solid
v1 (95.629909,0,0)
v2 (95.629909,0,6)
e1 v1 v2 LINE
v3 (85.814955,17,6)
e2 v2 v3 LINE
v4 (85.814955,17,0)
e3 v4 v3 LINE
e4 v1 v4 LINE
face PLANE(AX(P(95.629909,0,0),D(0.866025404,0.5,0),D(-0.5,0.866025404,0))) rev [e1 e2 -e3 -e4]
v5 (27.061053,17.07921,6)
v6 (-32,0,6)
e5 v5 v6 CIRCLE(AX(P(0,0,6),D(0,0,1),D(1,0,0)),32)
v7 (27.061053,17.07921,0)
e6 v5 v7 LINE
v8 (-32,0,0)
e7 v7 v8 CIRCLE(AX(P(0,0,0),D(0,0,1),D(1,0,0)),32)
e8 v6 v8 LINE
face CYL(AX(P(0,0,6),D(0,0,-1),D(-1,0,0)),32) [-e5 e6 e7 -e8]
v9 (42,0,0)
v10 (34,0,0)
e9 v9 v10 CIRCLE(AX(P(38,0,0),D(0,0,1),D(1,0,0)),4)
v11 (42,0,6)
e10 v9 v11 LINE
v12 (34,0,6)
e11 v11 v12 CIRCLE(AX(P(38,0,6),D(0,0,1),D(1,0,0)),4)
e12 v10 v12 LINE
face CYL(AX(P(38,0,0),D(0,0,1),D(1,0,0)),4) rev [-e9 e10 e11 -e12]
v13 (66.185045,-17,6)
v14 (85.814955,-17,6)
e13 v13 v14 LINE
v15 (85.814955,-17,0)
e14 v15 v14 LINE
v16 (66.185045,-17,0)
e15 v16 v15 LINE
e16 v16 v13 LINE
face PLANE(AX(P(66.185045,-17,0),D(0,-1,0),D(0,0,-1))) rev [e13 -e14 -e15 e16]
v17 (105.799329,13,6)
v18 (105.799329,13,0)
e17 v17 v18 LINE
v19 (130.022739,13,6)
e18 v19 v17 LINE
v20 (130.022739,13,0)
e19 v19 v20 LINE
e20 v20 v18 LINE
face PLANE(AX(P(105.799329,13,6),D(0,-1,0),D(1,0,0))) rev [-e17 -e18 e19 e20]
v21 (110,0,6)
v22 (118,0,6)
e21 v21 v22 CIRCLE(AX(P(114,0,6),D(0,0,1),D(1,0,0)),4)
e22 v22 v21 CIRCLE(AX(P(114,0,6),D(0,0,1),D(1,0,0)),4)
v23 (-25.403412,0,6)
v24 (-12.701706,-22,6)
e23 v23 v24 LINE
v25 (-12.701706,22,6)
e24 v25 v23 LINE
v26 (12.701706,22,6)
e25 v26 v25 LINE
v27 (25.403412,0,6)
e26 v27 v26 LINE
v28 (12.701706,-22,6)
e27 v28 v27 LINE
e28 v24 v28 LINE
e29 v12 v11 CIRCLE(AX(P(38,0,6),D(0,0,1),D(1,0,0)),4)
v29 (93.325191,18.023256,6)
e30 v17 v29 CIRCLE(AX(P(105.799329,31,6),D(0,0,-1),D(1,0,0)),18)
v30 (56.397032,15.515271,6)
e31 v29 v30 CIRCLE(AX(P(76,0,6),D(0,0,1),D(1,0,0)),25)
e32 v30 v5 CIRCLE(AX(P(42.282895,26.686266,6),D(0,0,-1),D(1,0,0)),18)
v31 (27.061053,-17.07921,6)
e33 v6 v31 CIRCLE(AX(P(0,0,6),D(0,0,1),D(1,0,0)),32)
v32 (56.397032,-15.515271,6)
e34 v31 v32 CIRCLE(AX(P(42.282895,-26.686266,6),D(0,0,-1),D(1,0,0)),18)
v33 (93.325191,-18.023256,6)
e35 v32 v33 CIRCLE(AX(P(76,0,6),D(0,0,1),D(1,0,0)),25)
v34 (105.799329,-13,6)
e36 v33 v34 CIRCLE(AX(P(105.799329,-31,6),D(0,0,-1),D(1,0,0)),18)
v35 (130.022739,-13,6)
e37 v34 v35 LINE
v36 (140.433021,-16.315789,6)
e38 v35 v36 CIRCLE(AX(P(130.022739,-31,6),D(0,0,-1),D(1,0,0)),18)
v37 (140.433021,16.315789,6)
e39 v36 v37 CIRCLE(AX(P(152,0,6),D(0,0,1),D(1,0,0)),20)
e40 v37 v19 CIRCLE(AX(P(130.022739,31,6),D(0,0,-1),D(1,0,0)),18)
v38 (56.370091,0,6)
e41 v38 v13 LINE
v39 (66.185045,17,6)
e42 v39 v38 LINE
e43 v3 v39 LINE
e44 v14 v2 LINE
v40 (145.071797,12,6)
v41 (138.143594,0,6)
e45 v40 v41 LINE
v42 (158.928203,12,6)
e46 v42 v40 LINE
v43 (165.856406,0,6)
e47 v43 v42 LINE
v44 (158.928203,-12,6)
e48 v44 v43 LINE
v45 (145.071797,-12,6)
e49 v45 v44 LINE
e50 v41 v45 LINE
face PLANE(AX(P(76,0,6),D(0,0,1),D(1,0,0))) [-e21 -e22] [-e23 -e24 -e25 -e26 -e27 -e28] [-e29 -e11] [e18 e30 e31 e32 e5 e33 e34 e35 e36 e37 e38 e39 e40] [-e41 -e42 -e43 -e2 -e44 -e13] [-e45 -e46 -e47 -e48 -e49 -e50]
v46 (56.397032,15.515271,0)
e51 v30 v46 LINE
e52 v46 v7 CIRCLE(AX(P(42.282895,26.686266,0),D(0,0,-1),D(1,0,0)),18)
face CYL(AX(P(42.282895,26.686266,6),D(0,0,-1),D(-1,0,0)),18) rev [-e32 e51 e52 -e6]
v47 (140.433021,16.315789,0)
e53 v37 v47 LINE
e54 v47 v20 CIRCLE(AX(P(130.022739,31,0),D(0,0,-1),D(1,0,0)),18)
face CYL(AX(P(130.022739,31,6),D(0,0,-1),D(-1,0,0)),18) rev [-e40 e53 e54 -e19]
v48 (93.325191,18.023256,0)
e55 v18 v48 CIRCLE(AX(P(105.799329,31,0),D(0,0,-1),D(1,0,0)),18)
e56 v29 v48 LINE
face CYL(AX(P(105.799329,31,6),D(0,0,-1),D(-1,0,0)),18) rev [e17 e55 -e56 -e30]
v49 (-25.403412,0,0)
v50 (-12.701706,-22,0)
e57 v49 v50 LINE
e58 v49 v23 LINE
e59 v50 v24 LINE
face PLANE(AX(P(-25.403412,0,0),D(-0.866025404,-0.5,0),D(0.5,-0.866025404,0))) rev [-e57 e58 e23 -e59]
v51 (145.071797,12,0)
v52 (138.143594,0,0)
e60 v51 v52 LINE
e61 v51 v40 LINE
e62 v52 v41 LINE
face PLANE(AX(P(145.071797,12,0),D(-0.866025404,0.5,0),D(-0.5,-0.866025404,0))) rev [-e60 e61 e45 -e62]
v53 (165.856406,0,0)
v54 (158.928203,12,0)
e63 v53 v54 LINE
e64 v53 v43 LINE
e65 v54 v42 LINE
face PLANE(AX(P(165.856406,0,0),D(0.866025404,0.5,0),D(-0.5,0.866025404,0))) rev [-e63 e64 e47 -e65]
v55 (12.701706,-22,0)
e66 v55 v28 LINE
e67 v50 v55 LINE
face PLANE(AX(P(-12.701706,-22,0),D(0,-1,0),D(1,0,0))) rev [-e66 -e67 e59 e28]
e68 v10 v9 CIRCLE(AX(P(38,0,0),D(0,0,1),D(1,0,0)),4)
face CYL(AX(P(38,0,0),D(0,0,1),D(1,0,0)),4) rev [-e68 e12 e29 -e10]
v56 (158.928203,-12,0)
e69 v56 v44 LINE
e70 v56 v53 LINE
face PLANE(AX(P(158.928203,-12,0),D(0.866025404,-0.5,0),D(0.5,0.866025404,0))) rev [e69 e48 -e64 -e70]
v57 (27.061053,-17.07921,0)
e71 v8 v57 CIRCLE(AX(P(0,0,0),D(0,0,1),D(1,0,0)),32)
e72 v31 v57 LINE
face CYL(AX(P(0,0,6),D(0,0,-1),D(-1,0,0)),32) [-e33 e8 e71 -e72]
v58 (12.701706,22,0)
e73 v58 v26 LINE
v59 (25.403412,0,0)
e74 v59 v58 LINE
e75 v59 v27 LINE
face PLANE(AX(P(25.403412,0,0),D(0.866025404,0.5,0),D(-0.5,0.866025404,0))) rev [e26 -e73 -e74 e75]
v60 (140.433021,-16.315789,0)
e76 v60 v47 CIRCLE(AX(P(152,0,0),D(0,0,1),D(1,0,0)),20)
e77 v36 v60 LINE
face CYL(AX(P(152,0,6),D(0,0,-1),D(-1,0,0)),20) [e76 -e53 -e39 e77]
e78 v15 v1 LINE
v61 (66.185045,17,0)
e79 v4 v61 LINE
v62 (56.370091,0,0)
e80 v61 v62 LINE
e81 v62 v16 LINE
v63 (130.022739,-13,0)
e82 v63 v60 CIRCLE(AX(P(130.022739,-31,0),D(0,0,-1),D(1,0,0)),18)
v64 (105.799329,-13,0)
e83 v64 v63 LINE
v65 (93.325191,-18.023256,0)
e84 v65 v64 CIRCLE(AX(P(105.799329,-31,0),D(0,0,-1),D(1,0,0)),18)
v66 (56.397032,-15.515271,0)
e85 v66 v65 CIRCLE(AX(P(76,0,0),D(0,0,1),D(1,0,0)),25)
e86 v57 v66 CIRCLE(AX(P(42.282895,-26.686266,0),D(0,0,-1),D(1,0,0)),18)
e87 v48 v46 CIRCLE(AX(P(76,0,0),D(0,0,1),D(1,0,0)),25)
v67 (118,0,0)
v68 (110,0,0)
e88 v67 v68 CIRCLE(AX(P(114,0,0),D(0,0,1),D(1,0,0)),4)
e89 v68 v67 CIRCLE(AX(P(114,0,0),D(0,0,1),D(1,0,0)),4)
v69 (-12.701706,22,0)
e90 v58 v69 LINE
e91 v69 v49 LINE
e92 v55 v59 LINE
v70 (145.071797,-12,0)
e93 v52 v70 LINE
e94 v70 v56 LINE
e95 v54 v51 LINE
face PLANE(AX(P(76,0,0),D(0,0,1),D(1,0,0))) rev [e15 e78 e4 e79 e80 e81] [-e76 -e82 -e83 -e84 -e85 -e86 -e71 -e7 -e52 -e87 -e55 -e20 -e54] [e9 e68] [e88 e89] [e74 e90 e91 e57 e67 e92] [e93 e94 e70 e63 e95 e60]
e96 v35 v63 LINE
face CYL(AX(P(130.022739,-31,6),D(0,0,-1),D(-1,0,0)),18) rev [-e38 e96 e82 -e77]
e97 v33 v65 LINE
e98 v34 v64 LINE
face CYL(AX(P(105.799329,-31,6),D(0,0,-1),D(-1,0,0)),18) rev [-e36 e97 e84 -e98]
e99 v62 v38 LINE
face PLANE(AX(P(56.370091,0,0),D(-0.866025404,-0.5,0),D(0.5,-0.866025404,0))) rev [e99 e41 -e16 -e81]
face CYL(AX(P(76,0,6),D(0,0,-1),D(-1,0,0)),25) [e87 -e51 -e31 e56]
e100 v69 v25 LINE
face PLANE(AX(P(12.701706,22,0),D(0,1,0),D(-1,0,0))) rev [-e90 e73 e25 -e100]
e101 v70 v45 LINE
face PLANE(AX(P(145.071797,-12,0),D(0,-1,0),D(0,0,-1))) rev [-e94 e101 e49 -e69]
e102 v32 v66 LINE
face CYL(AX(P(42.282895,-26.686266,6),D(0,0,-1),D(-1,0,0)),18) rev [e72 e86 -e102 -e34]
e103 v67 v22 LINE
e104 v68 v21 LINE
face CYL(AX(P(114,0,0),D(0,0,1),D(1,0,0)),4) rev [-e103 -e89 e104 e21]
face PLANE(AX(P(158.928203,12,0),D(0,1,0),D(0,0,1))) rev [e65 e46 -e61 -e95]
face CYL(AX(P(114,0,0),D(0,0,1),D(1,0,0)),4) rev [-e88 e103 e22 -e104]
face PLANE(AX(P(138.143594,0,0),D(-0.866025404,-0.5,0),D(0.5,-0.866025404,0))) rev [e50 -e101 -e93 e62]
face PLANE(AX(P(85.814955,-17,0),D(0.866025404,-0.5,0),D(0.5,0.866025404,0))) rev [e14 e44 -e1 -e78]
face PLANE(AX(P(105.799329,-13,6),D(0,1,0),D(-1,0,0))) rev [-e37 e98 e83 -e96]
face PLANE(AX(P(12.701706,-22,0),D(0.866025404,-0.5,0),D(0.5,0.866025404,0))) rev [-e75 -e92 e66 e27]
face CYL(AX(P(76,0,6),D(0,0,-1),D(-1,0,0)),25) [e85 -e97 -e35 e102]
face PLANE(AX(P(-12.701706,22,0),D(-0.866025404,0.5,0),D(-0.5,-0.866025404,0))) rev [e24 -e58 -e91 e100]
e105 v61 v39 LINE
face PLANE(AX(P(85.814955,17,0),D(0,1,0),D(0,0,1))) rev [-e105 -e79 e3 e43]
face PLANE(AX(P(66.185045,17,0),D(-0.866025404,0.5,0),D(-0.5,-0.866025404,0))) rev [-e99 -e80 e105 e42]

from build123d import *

# Parameters (mm, degrees)
SPANNER_PLATE_6MM_DEPTH        = 6
HEX_OPENINGS_44_34_24_AF_DEPTH = 176.054277297
WEB_HOLES_SKETCH_R             = 4
WEB_HOLES_2X_8_DEPTH           = 176.054277297


with BuildPart() as part:
    # Spanner Outline Sketch → Spanner Plate 6mm (new body)
    with BuildSketch(Plane.XY):
        with BuildLine():
            Line((105.799328852, -13), (130.022739024, -13))
            ThreePointArc((130.022739024, -13), (135.485531832, -13.848968115), (140.433020539, -16.315789474))
            ThreePointArc((140.433020539, -16.315789474), (172, 0), (140.433020539, 16.315789474))
            ThreePointArc((140.433020539, 16.315789474), (135.485531832, 13.848968115), (130.022739024, 13))
            Line((130.022739024, 13), (105.799328852, 13))
            ThreePointArc((105.799328852, 13), (99.075542543, 14.302973388), (93.325191193, 18.023255814))
            ThreePointArc((93.325191193, 18.023255814), (74.306021319, 24.942542698), (56.397031824, 15.515271144))
            ThreePointArc((56.397031824, 15.515271144), (41.324651991, 8.711790831), (27.061052632, 17.079210476))
            ThreePointArc((27.061052632, 17.079210476), (-32, 0), (27.061052632, -17.079210476))
            ThreePointArc((27.061052632, -17.079210476), (41.324651991, -8.711790831), (56.397031824, -15.515271144))
            ThreePointArc((56.397031824, -15.515271144), (74.306021319, -24.942542698), (93.325191193, -18.023255814))
            ThreePointArc((93.325191193, -18.023255814), (99.075542543, -14.302973388), (105.799328852, -13))
        make_face()
    extrude(amount=SPANNER_PLATE_6MM_DEPTH)

    # Hex Openings Sketch → Hex Openings 44-34-24 AF (cut, through all)
    with BuildSketch(Plane.XY.offset(6)):
        Polygon((25.403411844, 0), (12.701705922, 22), (-12.701705922, 22), (-25.403411844, 0), (-12.701705922, -22), (12.701705922, -22), align=None)
        Polygon((95.629909152, 0), (85.814954576, 17), (66.185045424, 17), (56.370090848, 0), (66.185045424, -17), (85.814954576, -17), align=None)
        Polygon((165.856406461, 0), (158.92820323, 12), (145.07179677, 12), (138.143593539, 0), (145.07179677, -12), (158.92820323, -12), align=None)
    extrude(amount=-HEX_OPENINGS_44_34_24_AF_DEPTH, mode=Mode.SUBTRACT)

    # Web Holes Sketch → Web Holes 2xØ8 (cut, through all)
    with BuildSketch(Plane.XY.offset(6)):
        with Locations((38, 0)):
            Circle(WEB_HOLES_SKETCH_R)
        with Locations((114, 0)):
            Circle(WEB_HOLES_SKETCH_R)
    extrude(amount=-WEB_HOLES_2X_8_DEPTH, mode=Mode.SUBTRACT)


solid = part.part
